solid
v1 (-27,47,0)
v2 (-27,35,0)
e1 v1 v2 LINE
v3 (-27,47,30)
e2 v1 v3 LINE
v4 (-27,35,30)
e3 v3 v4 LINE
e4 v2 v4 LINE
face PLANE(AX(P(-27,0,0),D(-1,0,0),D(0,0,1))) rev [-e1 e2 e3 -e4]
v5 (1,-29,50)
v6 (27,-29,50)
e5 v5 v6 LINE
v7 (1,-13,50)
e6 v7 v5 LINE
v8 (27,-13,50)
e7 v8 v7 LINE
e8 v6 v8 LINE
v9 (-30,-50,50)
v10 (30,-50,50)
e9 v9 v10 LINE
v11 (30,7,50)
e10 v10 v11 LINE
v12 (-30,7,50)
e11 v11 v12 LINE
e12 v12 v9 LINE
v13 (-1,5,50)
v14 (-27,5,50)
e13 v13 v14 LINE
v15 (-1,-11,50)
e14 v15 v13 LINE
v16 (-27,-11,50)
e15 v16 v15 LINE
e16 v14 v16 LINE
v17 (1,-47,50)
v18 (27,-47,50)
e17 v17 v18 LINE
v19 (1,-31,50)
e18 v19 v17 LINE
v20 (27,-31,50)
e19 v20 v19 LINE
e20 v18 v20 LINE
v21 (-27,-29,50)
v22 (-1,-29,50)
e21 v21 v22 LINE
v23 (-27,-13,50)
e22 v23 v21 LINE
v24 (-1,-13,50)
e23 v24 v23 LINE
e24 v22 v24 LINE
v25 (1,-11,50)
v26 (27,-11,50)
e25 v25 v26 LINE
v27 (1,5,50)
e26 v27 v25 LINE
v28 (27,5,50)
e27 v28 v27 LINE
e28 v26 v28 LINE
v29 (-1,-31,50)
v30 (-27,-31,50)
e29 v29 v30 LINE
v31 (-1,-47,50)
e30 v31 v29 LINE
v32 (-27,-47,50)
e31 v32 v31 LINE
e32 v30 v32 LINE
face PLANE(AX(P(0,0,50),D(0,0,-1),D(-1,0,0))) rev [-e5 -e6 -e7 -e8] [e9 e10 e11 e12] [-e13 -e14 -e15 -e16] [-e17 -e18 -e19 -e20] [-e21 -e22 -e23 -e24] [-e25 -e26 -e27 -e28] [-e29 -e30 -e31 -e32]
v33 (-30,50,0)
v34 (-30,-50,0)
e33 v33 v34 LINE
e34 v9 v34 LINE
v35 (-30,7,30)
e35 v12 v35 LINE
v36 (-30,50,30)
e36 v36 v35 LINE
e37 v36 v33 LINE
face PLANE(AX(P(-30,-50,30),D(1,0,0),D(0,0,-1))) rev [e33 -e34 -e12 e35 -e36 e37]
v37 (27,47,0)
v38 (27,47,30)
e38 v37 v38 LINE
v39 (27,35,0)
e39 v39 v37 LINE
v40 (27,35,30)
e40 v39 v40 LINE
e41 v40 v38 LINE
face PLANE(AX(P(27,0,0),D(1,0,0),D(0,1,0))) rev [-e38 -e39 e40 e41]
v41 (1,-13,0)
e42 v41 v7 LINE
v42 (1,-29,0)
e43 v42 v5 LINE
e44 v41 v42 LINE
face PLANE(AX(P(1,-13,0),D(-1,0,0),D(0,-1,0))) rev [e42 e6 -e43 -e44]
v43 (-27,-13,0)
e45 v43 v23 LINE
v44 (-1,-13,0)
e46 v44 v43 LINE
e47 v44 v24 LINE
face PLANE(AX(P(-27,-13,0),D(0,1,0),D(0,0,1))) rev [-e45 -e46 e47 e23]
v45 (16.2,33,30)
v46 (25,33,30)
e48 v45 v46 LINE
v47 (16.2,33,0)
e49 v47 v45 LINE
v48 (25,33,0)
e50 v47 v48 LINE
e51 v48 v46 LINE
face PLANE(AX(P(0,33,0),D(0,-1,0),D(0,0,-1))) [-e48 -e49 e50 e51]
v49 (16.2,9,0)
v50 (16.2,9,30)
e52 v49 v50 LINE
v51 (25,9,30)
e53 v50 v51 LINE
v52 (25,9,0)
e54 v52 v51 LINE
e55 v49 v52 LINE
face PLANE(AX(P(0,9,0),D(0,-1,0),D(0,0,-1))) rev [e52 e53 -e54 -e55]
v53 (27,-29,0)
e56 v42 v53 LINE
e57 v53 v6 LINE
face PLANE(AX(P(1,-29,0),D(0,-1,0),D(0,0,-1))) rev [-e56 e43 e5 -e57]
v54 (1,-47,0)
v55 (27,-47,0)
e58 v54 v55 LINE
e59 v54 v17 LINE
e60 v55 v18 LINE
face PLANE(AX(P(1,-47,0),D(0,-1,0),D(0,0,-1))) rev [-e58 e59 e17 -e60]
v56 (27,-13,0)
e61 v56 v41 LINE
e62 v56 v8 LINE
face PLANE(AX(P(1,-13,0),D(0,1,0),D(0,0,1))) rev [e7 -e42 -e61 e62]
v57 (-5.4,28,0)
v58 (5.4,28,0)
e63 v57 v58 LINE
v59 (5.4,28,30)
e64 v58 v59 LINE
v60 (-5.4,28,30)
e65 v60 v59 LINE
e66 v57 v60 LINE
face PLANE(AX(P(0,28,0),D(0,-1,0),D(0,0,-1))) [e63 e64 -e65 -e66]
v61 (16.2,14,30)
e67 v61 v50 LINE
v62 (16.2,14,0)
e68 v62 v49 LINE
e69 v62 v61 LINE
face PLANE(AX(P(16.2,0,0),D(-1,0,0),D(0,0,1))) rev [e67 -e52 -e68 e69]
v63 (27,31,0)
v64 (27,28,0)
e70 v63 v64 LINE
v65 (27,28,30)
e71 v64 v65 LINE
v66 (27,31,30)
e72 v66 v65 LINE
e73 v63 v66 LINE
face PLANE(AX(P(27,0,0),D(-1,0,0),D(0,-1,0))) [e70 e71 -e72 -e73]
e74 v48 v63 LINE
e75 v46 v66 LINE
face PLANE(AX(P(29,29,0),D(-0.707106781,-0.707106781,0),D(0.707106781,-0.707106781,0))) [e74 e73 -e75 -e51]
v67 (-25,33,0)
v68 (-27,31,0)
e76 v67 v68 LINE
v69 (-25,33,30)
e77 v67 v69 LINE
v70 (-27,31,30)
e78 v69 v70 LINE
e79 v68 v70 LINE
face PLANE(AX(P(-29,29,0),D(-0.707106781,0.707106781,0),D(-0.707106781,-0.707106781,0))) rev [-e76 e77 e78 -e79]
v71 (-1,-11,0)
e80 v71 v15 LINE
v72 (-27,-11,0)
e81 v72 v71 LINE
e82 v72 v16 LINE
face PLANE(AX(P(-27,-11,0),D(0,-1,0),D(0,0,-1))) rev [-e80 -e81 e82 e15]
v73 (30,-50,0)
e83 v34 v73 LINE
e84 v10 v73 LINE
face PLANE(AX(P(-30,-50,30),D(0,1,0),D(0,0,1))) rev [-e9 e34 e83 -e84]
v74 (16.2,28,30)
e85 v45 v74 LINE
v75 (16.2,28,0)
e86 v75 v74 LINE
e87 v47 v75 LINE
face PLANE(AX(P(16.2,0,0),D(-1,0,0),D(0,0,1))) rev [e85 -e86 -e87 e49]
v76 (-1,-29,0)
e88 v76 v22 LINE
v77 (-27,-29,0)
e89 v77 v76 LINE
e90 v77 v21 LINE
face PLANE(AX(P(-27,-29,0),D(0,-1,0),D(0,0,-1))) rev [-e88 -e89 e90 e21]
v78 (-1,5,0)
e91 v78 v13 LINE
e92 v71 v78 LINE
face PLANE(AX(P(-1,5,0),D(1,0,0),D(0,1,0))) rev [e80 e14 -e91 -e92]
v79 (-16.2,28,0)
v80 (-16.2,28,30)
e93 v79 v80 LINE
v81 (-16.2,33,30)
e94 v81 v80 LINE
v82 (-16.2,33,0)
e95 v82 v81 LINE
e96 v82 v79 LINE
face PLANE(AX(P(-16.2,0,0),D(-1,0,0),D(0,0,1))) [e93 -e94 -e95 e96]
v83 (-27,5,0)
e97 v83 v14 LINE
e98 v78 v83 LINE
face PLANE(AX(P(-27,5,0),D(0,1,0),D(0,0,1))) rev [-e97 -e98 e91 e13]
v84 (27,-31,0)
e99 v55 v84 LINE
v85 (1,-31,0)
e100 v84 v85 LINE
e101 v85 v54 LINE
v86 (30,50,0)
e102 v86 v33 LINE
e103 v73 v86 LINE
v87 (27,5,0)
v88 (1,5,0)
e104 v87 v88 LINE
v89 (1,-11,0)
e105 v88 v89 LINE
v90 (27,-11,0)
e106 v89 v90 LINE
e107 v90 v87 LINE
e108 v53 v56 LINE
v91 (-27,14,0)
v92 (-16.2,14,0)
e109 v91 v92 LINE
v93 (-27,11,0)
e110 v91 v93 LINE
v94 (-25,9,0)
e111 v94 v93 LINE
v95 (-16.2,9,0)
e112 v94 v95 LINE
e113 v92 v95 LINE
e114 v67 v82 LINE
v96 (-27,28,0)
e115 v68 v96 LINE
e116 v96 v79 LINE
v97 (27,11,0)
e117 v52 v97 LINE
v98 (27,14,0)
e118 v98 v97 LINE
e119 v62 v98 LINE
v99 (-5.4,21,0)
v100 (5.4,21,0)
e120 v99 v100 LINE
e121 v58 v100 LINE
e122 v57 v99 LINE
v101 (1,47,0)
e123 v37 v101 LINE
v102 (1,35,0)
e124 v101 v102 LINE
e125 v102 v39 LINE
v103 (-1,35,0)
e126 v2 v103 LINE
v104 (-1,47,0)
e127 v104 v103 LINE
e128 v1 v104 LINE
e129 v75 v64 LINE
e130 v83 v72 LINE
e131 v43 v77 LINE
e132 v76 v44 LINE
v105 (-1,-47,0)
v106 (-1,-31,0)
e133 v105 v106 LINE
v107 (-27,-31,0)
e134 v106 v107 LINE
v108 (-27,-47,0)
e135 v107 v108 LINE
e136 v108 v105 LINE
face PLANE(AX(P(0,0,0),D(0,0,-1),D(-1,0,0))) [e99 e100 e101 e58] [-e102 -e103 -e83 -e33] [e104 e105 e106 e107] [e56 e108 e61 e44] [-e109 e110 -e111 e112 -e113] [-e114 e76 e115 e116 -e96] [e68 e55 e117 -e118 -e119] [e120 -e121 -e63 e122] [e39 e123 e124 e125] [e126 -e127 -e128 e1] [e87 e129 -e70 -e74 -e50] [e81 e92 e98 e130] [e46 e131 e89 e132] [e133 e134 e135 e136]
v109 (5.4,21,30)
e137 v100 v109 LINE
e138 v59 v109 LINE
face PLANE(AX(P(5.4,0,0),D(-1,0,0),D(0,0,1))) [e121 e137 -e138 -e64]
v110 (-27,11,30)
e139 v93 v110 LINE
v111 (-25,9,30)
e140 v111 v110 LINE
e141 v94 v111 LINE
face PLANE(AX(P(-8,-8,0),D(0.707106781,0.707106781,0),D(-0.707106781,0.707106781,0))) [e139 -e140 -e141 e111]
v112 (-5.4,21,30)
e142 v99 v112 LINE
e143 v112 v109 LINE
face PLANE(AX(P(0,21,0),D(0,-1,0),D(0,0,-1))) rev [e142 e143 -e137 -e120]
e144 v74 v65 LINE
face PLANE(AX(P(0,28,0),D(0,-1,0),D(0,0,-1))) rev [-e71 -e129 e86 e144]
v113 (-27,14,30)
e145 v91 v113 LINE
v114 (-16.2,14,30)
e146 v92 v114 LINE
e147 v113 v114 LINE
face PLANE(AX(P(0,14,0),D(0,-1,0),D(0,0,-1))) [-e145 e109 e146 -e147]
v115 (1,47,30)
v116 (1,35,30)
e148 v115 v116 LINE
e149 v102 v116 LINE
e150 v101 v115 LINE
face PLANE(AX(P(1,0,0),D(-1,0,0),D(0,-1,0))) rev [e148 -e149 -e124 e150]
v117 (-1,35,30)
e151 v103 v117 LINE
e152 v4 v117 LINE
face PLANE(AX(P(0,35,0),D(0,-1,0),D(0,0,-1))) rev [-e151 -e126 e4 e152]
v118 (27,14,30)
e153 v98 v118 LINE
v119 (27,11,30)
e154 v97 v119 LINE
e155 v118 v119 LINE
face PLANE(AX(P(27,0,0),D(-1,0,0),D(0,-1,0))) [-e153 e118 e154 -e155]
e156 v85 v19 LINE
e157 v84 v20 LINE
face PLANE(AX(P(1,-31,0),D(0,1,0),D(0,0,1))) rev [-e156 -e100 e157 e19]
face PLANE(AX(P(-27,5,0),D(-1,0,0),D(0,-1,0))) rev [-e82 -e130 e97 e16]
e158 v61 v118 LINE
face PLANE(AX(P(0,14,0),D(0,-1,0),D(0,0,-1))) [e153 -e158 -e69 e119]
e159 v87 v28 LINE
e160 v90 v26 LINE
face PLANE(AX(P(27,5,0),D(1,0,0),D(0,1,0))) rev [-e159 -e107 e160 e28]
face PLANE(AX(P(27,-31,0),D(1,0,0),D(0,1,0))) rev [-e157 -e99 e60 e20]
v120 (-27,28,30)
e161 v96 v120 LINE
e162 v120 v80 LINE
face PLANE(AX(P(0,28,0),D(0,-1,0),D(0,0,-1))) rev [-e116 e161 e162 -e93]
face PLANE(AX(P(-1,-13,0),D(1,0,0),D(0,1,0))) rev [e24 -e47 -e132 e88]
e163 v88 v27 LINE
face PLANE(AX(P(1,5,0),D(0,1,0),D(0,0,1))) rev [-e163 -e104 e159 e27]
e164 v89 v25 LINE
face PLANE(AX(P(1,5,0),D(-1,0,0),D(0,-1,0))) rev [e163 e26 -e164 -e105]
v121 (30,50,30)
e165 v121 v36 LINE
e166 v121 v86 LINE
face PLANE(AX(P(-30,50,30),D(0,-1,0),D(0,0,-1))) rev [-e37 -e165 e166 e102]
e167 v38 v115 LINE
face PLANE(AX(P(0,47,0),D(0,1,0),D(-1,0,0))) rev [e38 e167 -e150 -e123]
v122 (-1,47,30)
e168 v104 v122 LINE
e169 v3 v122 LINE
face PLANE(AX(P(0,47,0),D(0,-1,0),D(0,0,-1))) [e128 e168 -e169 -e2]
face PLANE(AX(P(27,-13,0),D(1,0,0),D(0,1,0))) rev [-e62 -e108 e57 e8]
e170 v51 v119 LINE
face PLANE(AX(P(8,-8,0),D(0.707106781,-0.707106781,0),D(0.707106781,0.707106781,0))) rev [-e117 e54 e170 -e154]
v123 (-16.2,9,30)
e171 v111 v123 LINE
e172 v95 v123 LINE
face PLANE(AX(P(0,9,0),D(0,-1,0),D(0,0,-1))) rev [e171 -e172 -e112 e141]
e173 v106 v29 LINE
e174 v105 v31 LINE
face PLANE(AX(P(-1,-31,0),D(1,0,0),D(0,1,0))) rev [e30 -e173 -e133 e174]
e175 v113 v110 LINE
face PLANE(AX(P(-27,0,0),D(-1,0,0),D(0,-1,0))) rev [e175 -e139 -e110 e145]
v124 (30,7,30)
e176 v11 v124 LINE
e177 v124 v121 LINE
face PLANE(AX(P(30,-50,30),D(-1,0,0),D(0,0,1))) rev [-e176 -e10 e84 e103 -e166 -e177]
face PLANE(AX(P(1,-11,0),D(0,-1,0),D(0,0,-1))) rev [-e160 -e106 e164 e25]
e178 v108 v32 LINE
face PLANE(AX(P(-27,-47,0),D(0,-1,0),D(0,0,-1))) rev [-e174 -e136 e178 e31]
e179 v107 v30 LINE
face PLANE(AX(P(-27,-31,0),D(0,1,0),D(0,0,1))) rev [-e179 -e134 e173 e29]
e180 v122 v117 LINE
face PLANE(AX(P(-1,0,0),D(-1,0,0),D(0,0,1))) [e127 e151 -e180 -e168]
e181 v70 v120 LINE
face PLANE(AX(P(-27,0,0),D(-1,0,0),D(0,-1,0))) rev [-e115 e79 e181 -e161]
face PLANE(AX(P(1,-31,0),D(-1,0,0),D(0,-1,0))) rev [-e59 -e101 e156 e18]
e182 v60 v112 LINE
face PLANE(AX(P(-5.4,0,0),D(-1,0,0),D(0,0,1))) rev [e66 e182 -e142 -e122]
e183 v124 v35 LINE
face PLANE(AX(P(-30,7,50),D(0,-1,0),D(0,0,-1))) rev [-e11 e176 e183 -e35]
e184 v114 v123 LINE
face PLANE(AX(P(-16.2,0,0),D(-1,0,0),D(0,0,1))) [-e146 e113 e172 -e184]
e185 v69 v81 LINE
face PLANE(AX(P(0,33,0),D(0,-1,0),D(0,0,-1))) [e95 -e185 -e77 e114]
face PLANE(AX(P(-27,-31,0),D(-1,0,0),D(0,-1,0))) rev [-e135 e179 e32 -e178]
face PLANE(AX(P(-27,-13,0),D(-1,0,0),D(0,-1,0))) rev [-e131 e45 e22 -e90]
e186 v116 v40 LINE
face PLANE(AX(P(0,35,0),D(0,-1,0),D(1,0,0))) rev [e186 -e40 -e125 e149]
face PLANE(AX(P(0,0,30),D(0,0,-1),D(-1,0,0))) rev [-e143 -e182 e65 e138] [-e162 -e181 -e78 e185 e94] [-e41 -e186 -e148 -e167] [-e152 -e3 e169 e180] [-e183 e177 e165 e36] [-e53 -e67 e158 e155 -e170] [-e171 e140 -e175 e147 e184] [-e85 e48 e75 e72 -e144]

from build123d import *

# Parameters (mm, degrees)
BASE_BLOCK_SKETCH_W         = 60
BASE_BLOCK_SKETCH_H         = 100
BASE_BLOCK_DEPTH            = 30
LOWER_CELL_POCKETS_SKETCH_W = 26
LOWER_CELL_POCKETS_SKETCH_H = 12
LOWER_CELL_POCKETS_DEPTH    = 66.574385243
UPPER_STEP_SKETCH_W         = 60
UPPER_STEP_SKETCH_H         = 57
UPPER_STEP_BOSS_DEPTH       = 20
UPPER_CELL_POCKETS_SKETCH_W = 26
UPPER_CELL_POCKETS_SKETCH_H = 16
UPPER_CELL_POCKETS_DEPTH    = 77.811457479
BACK_WALL_SLOTS_SKETCH_W    = 10.8
BACK_WALL_SLOTS_SKETCH_H    = 7
BACK_WALL_SLOTS_DEPTH       = 66.574385243


with BuildPart() as part:
    # Base Block Sketch → Base Block (new body)
    with BuildSketch(Plane.XY):
        Rectangle(BASE_BLOCK_SKETCH_W, BASE_BLOCK_SKETCH_H)
    extrude(amount=BASE_BLOCK_DEPTH)

    # Lower Cell Pockets Sketch → Lower Cell Pockets (cut, through all)
    with BuildSketch(Plane.XY.offset(30)):
        with Locations((14, 41)):
            Rectangle(LOWER_CELL_POCKETS_SKETCH_W, LOWER_CELL_POCKETS_SKETCH_H)
        Polygon((-21.788065722, 47), (-27, 47), (-27, 35), (-1, 35), (-1, 47), align=None)
    extrude(amount=-LOWER_CELL_POCKETS_DEPTH, mode=Mode.SUBTRACT)

    # Upper Step Sketch → Upper Step Boss (add)
    with BuildSketch(Plane.XY.offset(30)):
        with Locations((0, -21.5)):
            Rectangle(UPPER_STEP_SKETCH_W, UPPER_STEP_SKETCH_H)
    extrude(amount=UPPER_STEP_BOSS_DEPTH)

    # Upper Cell Pockets Sketch → Upper Cell Pockets (cut, through all)
    with BuildSketch(Plane.XY.offset(50)):
        with Locations((-14, -3)):
            Rectangle(UPPER_CELL_POCKETS_SKETCH_W, UPPER_CELL_POCKETS_SKETCH_H)
        with Locations((14, -3)):
            Rectangle(UPPER_CELL_POCKETS_SKETCH_W, UPPER_CELL_POCKETS_SKETCH_H)
        with Locations((14, -21)):
            Rectangle(UPPER_CELL_POCKETS_SKETCH_W, UPPER_CELL_POCKETS_SKETCH_H)
        with Locations((14, -39)):
            Rectangle(UPPER_CELL_POCKETS_SKETCH_W, UPPER_CELL_POCKETS_SKETCH_H)
        with Locations((-14, -21)):
            Rectangle(UPPER_CELL_POCKETS_SKETCH_W, UPPER_CELL_POCKETS_SKETCH_H)
        with Locations((-14, -39)):
            Rectangle(UPPER_CELL_POCKETS_SKETCH_W, UPPER_CELL_POCKETS_SKETCH_H)
    extrude(amount=-UPPER_CELL_POCKETS_DEPTH, mode=Mode.SUBTRACT)

    # Back Wall Slots Sketch → Back Wall Slots (cut, through all)
    with BuildSketch(Plane.XY.offset(30)):
        Polygon((27, 14), (16.2, 14), (16.2, 9), (25, 9), (27, 11), align=None)
        with Locations((0, 24.5)):
            Rectangle(BACK_WALL_SLOTS_SKETCH_W, BACK_WALL_SLOTS_SKETCH_H)
        Polygon((-16.2, 33), (-25, 33), (-27, 31), (-27, 28), (-16.2, 28), align=None)
        Polygon((25, 33), (16.2, 33), (16.2, 28), (27, 28), (27, 31), align=None)
        Polygon((-16.2, 14), (-27, 14), (-27, 11), (-25, 9), (-16.2, 9), align=None)
    extrude(amount=-BACK_WALL_SLOTS_DEPTH, mode=Mode.SUBTRACT)


solid = part.part
